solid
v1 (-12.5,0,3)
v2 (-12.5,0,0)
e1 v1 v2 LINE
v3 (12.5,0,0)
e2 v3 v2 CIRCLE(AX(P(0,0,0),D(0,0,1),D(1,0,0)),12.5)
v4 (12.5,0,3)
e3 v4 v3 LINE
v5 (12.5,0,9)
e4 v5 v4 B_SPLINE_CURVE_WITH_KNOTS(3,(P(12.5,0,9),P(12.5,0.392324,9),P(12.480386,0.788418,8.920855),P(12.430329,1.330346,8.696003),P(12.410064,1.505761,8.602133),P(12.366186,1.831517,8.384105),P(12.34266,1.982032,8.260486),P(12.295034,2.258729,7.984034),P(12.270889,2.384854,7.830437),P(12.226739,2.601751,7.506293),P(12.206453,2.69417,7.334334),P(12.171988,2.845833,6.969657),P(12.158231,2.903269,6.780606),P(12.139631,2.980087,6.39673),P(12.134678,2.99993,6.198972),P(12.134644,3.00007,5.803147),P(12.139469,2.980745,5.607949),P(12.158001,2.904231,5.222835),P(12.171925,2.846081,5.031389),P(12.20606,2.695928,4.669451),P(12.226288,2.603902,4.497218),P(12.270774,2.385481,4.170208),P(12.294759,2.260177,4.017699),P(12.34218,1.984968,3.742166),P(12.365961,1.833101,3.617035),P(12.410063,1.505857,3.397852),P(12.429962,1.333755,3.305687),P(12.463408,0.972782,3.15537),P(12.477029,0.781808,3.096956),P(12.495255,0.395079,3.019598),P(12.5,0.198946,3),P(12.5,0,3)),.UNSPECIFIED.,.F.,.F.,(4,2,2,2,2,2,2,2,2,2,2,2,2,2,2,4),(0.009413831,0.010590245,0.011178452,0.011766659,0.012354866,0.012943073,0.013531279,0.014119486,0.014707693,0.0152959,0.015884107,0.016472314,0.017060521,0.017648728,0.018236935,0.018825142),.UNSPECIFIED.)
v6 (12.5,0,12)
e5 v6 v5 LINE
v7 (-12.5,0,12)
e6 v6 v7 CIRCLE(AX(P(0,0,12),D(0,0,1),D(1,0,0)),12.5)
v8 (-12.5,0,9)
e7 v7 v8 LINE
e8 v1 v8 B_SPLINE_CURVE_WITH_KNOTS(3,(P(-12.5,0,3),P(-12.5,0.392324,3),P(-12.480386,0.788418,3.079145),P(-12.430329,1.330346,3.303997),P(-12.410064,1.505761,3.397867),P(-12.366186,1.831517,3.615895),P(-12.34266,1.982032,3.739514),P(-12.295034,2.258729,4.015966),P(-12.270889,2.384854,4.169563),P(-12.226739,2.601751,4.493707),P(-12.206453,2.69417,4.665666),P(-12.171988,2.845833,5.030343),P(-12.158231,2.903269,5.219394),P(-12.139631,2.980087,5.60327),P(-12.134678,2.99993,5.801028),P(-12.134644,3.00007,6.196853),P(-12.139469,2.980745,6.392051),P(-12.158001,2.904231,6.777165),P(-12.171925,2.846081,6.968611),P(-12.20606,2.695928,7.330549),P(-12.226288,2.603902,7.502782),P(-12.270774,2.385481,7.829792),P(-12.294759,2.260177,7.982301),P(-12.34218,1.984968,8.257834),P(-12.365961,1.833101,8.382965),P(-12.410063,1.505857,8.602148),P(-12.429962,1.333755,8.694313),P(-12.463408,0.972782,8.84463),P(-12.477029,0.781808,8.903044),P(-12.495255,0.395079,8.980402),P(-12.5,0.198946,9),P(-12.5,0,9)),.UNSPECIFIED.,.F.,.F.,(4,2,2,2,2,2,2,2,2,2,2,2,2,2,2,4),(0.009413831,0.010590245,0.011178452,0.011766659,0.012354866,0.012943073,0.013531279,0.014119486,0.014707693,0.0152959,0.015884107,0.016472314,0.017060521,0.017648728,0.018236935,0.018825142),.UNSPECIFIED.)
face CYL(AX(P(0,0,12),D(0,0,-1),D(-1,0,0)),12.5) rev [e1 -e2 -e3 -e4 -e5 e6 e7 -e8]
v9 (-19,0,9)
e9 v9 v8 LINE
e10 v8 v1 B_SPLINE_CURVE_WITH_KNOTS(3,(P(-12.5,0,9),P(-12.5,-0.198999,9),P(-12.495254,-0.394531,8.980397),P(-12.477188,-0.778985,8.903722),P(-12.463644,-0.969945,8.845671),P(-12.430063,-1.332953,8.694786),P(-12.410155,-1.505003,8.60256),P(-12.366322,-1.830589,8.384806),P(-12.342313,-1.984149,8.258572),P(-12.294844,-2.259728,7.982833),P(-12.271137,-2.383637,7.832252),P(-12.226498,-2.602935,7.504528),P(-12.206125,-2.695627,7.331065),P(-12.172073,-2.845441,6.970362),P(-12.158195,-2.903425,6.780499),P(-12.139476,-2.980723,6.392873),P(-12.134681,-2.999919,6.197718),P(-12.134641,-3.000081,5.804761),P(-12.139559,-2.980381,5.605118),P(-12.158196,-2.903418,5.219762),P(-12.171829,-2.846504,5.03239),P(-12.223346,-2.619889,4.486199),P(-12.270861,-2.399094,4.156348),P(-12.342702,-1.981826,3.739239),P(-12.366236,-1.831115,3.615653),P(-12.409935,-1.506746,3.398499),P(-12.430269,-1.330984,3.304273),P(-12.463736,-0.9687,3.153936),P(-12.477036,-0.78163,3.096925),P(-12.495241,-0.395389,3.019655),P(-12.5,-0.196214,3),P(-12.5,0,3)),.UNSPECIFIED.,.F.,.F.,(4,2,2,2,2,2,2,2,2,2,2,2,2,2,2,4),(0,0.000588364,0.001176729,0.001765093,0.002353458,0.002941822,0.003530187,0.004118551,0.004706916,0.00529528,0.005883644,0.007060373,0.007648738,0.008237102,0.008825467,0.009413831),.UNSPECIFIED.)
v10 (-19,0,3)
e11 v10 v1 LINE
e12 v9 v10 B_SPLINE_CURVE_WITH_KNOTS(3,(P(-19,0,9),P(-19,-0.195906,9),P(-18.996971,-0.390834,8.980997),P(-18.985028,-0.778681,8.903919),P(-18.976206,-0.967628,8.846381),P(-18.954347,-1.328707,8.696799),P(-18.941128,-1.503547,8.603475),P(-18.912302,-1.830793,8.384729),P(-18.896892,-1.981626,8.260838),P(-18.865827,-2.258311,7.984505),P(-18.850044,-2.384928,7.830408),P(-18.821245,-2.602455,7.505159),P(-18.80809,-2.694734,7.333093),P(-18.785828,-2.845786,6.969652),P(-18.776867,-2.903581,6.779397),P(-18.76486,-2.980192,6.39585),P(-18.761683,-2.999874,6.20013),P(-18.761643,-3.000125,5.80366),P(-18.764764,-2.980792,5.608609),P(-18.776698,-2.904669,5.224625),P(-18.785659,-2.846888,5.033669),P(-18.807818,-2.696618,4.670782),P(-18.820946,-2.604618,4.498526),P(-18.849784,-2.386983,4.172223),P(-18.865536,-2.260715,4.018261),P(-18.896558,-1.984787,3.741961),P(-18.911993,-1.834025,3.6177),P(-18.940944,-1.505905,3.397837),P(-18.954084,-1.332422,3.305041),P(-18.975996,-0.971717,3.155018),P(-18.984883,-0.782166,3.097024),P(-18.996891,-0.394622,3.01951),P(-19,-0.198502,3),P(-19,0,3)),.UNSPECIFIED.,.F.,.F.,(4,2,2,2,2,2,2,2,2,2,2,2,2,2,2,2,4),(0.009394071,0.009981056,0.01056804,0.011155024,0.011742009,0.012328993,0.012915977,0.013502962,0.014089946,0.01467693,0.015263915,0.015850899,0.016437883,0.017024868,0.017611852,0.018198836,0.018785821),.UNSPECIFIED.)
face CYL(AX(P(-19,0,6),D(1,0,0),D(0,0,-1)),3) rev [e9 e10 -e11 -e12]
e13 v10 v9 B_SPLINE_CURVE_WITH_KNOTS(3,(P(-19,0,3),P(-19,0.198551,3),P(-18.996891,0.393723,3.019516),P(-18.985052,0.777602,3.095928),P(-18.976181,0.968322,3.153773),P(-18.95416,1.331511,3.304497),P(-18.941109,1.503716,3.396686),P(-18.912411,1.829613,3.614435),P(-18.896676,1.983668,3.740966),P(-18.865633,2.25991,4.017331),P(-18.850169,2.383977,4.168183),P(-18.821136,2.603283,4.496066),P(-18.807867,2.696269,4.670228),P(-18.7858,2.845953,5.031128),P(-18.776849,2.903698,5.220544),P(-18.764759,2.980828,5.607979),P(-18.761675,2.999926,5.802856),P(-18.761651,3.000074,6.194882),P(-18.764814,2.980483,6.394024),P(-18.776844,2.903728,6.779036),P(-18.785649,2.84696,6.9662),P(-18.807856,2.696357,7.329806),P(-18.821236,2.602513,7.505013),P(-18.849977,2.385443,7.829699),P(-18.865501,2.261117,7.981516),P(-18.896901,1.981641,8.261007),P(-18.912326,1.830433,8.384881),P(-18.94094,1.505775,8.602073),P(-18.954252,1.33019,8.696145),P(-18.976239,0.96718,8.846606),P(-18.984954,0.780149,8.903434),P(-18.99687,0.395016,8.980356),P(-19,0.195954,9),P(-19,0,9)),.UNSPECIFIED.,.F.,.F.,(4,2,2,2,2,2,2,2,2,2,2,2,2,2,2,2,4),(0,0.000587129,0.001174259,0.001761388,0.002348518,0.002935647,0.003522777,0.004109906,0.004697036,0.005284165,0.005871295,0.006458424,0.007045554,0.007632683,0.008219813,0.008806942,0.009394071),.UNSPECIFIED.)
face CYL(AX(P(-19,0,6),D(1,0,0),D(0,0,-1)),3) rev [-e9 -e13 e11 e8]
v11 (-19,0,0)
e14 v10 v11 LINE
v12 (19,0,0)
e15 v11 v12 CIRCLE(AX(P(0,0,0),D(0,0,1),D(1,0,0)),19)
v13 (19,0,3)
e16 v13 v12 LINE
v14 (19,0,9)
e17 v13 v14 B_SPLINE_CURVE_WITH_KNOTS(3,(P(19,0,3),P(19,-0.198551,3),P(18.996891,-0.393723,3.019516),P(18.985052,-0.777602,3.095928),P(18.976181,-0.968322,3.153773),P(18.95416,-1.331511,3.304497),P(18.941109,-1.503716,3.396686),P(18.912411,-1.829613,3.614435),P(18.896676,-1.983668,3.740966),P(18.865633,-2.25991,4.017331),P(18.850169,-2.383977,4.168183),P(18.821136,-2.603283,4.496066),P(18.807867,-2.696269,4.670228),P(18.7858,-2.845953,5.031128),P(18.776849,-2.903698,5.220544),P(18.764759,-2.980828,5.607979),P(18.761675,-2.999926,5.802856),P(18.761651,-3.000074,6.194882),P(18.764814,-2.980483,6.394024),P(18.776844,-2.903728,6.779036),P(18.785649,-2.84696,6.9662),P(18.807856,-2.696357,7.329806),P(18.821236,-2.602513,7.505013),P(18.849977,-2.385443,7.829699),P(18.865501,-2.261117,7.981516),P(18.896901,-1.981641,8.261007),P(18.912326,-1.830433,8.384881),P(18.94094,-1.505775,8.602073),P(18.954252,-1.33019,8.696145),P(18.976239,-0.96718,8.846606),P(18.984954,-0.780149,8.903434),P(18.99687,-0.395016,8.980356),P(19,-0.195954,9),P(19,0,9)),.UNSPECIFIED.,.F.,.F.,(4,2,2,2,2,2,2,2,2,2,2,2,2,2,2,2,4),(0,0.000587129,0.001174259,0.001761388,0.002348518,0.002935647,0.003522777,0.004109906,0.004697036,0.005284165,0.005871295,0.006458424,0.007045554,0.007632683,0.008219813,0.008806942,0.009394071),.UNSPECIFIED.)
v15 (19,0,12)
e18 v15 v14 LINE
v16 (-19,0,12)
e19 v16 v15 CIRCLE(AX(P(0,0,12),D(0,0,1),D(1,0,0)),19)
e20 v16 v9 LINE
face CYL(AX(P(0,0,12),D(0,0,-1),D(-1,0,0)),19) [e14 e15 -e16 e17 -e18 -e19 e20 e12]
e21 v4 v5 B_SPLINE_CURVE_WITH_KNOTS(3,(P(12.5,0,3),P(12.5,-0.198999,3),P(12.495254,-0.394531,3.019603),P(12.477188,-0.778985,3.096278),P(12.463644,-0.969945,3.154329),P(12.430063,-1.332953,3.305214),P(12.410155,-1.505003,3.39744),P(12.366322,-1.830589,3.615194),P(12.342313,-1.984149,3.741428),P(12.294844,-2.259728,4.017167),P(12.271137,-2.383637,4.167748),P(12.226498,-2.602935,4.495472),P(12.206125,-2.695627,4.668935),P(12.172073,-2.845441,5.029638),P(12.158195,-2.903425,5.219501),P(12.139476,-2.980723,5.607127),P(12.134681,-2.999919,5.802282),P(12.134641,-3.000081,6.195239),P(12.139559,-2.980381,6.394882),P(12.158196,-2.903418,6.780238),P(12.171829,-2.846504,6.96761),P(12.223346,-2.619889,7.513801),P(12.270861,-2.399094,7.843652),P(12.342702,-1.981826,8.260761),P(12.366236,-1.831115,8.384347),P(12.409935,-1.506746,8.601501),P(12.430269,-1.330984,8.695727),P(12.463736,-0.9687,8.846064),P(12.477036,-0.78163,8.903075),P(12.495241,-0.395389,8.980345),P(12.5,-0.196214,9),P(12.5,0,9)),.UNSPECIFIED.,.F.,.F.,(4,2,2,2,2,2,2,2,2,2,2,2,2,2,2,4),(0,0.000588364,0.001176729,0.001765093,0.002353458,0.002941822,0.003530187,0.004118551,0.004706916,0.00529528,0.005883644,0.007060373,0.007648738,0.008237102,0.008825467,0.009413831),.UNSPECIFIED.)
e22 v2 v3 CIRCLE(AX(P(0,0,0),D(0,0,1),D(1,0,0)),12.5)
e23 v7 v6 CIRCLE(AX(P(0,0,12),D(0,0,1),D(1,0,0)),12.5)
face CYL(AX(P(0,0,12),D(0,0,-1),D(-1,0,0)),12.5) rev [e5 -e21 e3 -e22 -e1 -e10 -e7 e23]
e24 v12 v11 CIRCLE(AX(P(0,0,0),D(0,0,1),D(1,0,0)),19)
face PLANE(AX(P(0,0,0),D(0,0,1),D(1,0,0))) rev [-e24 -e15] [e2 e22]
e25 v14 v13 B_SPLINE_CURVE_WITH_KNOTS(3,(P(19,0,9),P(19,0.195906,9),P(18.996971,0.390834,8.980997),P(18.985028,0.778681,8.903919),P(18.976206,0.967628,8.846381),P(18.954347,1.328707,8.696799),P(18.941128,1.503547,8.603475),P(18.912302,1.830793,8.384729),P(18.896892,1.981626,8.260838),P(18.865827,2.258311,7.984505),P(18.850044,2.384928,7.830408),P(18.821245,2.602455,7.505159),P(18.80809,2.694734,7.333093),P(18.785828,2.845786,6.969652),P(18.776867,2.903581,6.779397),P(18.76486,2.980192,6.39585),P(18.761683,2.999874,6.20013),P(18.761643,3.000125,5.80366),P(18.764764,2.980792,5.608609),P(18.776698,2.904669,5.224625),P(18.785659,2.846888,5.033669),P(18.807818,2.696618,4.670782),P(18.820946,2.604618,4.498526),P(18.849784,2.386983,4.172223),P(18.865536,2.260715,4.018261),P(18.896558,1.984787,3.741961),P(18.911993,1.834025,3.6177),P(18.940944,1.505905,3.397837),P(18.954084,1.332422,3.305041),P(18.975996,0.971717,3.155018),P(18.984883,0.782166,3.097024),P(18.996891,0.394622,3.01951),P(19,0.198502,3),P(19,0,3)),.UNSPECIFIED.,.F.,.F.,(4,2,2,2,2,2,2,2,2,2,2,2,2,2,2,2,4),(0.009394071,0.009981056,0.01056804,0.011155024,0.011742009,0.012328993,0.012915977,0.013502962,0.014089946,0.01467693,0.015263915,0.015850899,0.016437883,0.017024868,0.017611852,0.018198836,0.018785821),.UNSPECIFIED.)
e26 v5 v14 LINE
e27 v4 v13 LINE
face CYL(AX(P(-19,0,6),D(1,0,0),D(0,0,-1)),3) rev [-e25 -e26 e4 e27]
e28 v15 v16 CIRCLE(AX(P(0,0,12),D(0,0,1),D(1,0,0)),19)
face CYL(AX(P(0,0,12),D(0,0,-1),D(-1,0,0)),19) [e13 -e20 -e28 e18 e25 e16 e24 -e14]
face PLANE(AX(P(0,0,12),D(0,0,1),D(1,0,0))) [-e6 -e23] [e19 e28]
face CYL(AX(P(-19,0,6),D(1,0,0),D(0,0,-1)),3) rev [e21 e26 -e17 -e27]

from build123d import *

# Parameters (mm, degrees)
COLLAR_RING_PROFILE_R       = 19
COLLAR_RING_PROFILE_R_2     = 12.5
COLLAR_RING_38X_25X12_DEPTH = 12
CROSS_HOLE_6_DEPTH          = 30.427877939
CROSS_HOLE_6_DEPTH_BACK     = 30.427877939
CROSS_HOLE_PROFILE_R        = 3


with BuildPart() as part:
    # Collar Ring Profile → Collar Ring Ø38xØ25x12 (new body)
    with BuildSketch(Plane.XY):
        Circle(COLLAR_RING_PROFILE_R)
        Circle(COLLAR_RING_PROFILE_R_2, mode=Mode.SUBTRACT)
    extrude(amount=COLLAR_RING_38X_25X12_DEPTH)

    # Cross Hole Profile → Cross Hole Ø6 (cut, two sides: drawn at the far end of the back side and taken through both)
    with BuildSketch(Plane(origin=(0, 0, 0), x_dir=(0, 0, -1), z_dir=(1, 0, 0)).offset(-CROSS_HOLE_6_DEPTH_BACK)):
        with Locations((-6, 0)):
            Circle(CROSS_HOLE_PROFILE_R)
    extrude(amount=CROSS_HOLE_6_DEPTH + CROSS_HOLE_6_DEPTH_BACK, mode=Mode.SUBTRACT)


solid = part.part
